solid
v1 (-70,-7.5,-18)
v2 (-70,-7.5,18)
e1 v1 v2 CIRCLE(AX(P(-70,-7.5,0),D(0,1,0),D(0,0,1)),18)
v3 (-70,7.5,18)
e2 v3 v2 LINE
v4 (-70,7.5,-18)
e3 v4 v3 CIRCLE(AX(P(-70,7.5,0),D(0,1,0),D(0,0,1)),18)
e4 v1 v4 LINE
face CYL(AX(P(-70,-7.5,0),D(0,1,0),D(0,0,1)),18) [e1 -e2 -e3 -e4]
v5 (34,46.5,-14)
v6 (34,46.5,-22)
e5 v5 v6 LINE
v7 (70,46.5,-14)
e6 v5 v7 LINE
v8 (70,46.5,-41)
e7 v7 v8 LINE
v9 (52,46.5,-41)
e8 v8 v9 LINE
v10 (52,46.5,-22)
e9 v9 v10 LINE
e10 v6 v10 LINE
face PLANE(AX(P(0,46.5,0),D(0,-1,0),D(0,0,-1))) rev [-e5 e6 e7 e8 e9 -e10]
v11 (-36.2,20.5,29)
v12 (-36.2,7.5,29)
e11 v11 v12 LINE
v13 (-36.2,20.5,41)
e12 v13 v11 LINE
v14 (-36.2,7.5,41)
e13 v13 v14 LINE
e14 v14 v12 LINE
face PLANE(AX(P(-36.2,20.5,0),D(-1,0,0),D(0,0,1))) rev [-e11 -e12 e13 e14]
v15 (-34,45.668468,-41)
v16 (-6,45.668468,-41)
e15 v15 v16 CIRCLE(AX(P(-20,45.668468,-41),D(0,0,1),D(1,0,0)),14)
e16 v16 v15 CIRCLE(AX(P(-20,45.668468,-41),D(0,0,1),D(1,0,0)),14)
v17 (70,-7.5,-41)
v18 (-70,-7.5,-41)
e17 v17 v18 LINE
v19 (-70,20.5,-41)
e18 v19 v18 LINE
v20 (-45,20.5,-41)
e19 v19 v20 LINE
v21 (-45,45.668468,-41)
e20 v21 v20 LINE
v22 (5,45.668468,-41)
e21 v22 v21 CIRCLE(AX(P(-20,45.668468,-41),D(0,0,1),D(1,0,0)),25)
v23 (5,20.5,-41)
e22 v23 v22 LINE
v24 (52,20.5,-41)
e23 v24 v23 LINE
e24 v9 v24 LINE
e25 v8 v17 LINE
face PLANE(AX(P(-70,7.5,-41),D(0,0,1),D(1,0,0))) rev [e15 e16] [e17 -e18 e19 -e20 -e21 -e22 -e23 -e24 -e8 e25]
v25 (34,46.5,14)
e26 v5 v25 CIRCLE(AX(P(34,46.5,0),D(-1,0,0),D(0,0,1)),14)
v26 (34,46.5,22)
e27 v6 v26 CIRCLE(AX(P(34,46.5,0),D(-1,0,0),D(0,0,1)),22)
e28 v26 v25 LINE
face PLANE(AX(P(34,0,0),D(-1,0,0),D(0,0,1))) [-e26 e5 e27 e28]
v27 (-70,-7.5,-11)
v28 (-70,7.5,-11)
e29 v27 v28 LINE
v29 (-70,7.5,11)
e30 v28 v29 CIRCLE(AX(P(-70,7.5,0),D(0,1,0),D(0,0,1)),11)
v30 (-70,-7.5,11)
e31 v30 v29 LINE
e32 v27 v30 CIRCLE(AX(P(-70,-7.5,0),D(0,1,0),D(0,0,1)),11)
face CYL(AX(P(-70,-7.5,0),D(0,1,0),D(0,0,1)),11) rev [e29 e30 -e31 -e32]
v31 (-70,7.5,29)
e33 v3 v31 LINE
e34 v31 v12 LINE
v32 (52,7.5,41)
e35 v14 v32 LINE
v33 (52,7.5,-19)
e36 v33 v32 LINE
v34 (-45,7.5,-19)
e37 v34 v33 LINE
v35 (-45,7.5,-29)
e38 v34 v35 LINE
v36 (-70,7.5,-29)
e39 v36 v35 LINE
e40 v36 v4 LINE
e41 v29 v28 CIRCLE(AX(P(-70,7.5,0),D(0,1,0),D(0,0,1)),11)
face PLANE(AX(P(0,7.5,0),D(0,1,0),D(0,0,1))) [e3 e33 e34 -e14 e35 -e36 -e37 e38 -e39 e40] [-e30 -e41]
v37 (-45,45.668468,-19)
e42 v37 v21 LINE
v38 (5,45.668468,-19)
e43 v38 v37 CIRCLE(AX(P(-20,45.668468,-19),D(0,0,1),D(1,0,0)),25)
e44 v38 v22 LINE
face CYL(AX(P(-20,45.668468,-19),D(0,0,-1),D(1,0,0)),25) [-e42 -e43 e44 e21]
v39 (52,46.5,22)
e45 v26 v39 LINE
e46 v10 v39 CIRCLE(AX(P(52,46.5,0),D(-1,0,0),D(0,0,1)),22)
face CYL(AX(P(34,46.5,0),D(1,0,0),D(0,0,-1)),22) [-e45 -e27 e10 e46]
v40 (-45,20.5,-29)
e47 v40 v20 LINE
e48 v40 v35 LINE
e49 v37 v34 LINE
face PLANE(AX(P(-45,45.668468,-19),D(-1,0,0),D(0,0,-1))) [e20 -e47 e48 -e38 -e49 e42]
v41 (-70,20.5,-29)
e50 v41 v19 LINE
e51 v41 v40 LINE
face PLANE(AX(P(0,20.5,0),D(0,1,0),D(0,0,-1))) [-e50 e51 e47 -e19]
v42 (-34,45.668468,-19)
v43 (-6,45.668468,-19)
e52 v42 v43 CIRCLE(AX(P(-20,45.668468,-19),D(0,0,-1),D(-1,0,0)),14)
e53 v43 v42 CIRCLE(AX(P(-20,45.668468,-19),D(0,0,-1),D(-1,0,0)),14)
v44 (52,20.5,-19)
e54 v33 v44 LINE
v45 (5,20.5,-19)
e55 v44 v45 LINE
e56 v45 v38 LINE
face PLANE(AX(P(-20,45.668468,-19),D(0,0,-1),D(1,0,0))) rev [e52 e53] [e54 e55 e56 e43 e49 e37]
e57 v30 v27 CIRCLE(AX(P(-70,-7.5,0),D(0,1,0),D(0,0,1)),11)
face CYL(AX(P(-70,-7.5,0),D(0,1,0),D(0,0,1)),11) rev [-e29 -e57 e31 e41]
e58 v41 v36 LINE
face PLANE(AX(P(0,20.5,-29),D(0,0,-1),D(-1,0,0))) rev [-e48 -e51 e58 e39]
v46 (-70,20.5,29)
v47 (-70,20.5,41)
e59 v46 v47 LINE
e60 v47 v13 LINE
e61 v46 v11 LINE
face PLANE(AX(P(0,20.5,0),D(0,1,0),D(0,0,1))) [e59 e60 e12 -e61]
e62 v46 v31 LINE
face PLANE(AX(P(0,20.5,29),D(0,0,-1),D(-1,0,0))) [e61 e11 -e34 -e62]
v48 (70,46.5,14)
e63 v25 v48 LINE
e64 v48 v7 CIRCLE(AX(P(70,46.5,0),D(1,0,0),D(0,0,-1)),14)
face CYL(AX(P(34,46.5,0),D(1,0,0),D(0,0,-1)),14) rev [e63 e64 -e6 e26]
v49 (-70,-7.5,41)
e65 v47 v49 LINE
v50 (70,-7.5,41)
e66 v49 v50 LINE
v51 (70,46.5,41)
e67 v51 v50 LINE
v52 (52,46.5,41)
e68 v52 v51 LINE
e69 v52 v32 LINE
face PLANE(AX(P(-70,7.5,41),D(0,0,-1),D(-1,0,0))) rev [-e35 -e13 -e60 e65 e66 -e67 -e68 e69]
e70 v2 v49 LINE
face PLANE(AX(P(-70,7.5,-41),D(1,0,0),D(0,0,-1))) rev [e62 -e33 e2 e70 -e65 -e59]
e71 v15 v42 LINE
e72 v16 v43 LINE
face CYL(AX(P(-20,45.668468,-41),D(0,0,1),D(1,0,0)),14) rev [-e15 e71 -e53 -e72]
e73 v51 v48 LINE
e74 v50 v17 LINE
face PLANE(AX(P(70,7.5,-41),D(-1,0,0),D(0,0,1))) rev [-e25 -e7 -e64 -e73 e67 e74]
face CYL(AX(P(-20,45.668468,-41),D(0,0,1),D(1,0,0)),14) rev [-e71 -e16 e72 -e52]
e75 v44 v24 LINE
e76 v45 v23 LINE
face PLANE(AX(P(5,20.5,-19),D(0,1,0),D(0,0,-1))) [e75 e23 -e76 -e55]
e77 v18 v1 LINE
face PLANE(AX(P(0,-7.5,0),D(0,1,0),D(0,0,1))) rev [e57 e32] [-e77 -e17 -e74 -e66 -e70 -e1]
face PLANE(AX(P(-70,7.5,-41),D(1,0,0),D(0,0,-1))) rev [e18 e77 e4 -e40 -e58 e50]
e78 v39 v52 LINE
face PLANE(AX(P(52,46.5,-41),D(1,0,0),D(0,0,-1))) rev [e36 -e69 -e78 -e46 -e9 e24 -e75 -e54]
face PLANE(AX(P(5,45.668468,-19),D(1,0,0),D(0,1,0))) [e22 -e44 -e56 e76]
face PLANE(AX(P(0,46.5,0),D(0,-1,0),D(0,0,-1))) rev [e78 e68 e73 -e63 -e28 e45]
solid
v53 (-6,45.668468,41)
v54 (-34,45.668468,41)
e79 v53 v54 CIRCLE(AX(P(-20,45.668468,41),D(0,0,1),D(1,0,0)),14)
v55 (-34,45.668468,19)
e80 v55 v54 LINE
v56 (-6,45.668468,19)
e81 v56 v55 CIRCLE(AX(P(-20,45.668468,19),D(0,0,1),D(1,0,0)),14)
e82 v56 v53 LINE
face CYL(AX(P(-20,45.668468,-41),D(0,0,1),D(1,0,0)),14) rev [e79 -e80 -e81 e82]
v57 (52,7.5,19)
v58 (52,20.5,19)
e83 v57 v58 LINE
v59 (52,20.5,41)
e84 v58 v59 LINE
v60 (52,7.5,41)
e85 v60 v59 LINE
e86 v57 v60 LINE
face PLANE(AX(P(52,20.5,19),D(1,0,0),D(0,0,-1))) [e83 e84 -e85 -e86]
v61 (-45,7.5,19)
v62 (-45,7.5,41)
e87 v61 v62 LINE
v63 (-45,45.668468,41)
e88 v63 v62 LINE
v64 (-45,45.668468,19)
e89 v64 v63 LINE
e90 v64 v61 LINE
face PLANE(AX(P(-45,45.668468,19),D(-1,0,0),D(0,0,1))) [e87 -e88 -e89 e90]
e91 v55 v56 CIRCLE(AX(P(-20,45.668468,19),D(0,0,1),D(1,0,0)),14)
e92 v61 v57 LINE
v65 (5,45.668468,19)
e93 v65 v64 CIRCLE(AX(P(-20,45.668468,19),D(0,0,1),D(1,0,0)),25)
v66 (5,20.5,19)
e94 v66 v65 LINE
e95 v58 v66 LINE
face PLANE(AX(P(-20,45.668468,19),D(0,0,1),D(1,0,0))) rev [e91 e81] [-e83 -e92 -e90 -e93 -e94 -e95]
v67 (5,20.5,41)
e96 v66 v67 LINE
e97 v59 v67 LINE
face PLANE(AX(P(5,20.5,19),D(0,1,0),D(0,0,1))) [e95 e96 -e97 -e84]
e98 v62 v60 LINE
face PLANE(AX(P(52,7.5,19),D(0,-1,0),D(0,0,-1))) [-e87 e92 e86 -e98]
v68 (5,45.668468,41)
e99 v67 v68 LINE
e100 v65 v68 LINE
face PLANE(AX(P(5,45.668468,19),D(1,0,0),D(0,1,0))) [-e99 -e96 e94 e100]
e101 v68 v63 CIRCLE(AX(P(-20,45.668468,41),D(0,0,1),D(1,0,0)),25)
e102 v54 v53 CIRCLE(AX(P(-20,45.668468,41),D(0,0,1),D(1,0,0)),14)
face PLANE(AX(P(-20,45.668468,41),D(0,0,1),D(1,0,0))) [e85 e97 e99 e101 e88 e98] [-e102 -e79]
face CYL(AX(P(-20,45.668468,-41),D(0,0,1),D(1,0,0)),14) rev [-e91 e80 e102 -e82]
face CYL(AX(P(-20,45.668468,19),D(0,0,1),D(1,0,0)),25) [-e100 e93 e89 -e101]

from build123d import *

# Parameters (mm, degrees)
BASE_PLATE_SKETCH_W        = 140
BASE_PLATE_SKETCH_H        = 82
BASE_PLATE_140X82X15_DEPTH = 7.5
SIDE_WALL_SKETCH_W         = 18
SIDE_WALL_SKETCH_H         = 82
SIDE_WALL_DEPTH            = 39
WALL_EXTENSION_DEPTH       = 18
WALL_SLOT_CUT_DEPTH        = 18
END_BLOCK_DEPTH            = 13
BEARING_LUG_DEPTH          = 22
LUG_BORE_DEPTH             = 129.91094718
LUG_BORE_DEPTH_BACK        = 129.91094718
LUG_BORE_SKETCH_R          = 14
CRADLE_BOSS_SKETCH_R       = 18
CRADLE_BOSS_DEPTH          = 15
CRADLE_SKETCH_R            = 11
CRADLE_CUT_DEPTH           = 15


with BuildPart() as part:
    # Base Plate Sketch → Base Plate 140x82x15 (new, symmetric)
    with BuildSketch(Plane(origin=(0, 0, 0), x_dir=(1, 0, 0), z_dir=(0, 1, 0))):
        Rectangle(BASE_PLATE_SKETCH_W, BASE_PLATE_SKETCH_H)
    extrude(amount=BASE_PLATE_140X82X15_DEPTH, both=True)

    # Side Wall Sketch → Side Wall (add)
    with BuildSketch(Plane(origin=(0, 7.5, 0), x_dir=(1, 0, 0), z_dir=(0, 1, 0))):
        with Locations((61, 0)):
            Rectangle(SIDE_WALL_SKETCH_W, SIDE_WALL_SKETCH_H)
    extrude(amount=SIDE_WALL_DEPTH)

    # Wall Extension Sketch → Wall Extension (add)
    with BuildSketch(Plane.ZY.offset(-52)):
        with BuildLine():
            Line((-14, 46.5), (-22, 46.5))
            ThreePointArc((-22, 46.5), (0, 24.5), (22, 46.5))
            Line((22, 46.5), (14, 46.5))
            ThreePointArc((14, 46.5), (0, 32.5), (-14, 46.5))
        make_face()
    extrude(amount=WALL_EXTENSION_DEPTH)

    # Wall Slot Sketch → Wall Slot Cut (cut)
    with BuildSketch(Plane(origin=(70, 0, 0), x_dir=(0, 0, -1), z_dir=(1, 0, 0))):
        with BuildLine():
            Line((-14, 46.5), (14, 46.5))
            ThreePointArc((14, 46.5), (0, 32.5), (-14, 46.5))
        make_face()
    extrude(amount=-WALL_SLOT_CUT_DEPTH, mode=Mode.SUBTRACT)

    # End Block Sketch → End Block (add)
    with BuildSketch(Plane(origin=(0, 7.5, 0), x_dir=(1, 0, 0), z_dir=(0, 1, 0))):
        Polygon((-70, -38.536273507), (-70, -41), (-36.2, -41), (-36.2, -29), (-70, -29), (-70, -37.053252514), align=None)
    end_block = extrude(amount=END_BLOCK_DEPTH)


with BuildPart() as body_2:
    # Bearing Lug Sketch → Bearing Lug (new body)
    with BuildSketch(Plane.XY.offset(41)):
        with BuildLine():
            Line((-45, 45.668467528), (-45, 7.5))
            Line((-45, 7.5), (52, 7.5))
            Line((52, 7.5), (52, 20.5))
            Line((52, 20.5), (5, 20.5))
            Line((5, 20.5), (5, 45.668467528))
            ThreePointArc((5, 45.668467528), (-20, 70.668467528), (-45, 45.668467528))
        make_face()
    bearing_lug = extrude(amount=-BEARING_LUG_DEPTH)


with BuildPart() as part_1:
    add(part.part)

    # Bearing Lug Mirror: Bearing Lug across plane
    add(bearing_lug.mirror(Plane.XY))

    # End Block Mirror: End Block across plane
    add(end_block.mirror(Plane.XY))


with BuildPart() as lug_bore_tool:
    # Lug Bore Sketch → Lug Bore (new, two sides: drawn at the far end of the back side and taken through both)
    with BuildSketch(Plane.XY.offset(41).offset(-LUG_BORE_DEPTH_BACK)):
        with Locations((-20, 45.668467528)):
            Circle(LUG_BORE_SKETCH_R)
    extrude(amount=LUG_BORE_DEPTH + LUG_BORE_DEPTH_BACK)


with BuildPart() as part_2:
    add(part_1.part)

    # Lug Bore: cut by lug_bore_tool
    add(lug_bore_tool.part, mode=Mode.SUBTRACT)

    # Cradle Boss Sketch → Cradle Boss (add)
    with BuildSketch(Plane(origin=(0, 7.5, 0), x_dir=(1, 0, 0), z_dir=(0, 1, 0))):
        with Locations((-70, 0)):
            Circle(CRADLE_BOSS_SKETCH_R)
    extrude(amount=-CRADLE_BOSS_DEPTH)

    # Cradle Sketch → Cradle Cut (cut)
    with BuildSketch(Plane(origin=(0, 7.5, 0), x_dir=(1, 0, 0), z_dir=(0, 1, 0))):
        with Locations(Location((-70, 0, 0), (0, 0, 270))):
            Circle(CRADLE_SKETCH_R)
    extrude(amount=-CRADLE_CUT_DEPTH, mode=Mode.SUBTRACT)


with BuildPart() as body_2_1:
    add(body_2.part)

    # Lug Bore: cut by lug_bore_tool
    add(lug_bore_tool.part, mode=Mode.SUBTRACT)


solid = Compound([part_2.part, body_2_1.part])
